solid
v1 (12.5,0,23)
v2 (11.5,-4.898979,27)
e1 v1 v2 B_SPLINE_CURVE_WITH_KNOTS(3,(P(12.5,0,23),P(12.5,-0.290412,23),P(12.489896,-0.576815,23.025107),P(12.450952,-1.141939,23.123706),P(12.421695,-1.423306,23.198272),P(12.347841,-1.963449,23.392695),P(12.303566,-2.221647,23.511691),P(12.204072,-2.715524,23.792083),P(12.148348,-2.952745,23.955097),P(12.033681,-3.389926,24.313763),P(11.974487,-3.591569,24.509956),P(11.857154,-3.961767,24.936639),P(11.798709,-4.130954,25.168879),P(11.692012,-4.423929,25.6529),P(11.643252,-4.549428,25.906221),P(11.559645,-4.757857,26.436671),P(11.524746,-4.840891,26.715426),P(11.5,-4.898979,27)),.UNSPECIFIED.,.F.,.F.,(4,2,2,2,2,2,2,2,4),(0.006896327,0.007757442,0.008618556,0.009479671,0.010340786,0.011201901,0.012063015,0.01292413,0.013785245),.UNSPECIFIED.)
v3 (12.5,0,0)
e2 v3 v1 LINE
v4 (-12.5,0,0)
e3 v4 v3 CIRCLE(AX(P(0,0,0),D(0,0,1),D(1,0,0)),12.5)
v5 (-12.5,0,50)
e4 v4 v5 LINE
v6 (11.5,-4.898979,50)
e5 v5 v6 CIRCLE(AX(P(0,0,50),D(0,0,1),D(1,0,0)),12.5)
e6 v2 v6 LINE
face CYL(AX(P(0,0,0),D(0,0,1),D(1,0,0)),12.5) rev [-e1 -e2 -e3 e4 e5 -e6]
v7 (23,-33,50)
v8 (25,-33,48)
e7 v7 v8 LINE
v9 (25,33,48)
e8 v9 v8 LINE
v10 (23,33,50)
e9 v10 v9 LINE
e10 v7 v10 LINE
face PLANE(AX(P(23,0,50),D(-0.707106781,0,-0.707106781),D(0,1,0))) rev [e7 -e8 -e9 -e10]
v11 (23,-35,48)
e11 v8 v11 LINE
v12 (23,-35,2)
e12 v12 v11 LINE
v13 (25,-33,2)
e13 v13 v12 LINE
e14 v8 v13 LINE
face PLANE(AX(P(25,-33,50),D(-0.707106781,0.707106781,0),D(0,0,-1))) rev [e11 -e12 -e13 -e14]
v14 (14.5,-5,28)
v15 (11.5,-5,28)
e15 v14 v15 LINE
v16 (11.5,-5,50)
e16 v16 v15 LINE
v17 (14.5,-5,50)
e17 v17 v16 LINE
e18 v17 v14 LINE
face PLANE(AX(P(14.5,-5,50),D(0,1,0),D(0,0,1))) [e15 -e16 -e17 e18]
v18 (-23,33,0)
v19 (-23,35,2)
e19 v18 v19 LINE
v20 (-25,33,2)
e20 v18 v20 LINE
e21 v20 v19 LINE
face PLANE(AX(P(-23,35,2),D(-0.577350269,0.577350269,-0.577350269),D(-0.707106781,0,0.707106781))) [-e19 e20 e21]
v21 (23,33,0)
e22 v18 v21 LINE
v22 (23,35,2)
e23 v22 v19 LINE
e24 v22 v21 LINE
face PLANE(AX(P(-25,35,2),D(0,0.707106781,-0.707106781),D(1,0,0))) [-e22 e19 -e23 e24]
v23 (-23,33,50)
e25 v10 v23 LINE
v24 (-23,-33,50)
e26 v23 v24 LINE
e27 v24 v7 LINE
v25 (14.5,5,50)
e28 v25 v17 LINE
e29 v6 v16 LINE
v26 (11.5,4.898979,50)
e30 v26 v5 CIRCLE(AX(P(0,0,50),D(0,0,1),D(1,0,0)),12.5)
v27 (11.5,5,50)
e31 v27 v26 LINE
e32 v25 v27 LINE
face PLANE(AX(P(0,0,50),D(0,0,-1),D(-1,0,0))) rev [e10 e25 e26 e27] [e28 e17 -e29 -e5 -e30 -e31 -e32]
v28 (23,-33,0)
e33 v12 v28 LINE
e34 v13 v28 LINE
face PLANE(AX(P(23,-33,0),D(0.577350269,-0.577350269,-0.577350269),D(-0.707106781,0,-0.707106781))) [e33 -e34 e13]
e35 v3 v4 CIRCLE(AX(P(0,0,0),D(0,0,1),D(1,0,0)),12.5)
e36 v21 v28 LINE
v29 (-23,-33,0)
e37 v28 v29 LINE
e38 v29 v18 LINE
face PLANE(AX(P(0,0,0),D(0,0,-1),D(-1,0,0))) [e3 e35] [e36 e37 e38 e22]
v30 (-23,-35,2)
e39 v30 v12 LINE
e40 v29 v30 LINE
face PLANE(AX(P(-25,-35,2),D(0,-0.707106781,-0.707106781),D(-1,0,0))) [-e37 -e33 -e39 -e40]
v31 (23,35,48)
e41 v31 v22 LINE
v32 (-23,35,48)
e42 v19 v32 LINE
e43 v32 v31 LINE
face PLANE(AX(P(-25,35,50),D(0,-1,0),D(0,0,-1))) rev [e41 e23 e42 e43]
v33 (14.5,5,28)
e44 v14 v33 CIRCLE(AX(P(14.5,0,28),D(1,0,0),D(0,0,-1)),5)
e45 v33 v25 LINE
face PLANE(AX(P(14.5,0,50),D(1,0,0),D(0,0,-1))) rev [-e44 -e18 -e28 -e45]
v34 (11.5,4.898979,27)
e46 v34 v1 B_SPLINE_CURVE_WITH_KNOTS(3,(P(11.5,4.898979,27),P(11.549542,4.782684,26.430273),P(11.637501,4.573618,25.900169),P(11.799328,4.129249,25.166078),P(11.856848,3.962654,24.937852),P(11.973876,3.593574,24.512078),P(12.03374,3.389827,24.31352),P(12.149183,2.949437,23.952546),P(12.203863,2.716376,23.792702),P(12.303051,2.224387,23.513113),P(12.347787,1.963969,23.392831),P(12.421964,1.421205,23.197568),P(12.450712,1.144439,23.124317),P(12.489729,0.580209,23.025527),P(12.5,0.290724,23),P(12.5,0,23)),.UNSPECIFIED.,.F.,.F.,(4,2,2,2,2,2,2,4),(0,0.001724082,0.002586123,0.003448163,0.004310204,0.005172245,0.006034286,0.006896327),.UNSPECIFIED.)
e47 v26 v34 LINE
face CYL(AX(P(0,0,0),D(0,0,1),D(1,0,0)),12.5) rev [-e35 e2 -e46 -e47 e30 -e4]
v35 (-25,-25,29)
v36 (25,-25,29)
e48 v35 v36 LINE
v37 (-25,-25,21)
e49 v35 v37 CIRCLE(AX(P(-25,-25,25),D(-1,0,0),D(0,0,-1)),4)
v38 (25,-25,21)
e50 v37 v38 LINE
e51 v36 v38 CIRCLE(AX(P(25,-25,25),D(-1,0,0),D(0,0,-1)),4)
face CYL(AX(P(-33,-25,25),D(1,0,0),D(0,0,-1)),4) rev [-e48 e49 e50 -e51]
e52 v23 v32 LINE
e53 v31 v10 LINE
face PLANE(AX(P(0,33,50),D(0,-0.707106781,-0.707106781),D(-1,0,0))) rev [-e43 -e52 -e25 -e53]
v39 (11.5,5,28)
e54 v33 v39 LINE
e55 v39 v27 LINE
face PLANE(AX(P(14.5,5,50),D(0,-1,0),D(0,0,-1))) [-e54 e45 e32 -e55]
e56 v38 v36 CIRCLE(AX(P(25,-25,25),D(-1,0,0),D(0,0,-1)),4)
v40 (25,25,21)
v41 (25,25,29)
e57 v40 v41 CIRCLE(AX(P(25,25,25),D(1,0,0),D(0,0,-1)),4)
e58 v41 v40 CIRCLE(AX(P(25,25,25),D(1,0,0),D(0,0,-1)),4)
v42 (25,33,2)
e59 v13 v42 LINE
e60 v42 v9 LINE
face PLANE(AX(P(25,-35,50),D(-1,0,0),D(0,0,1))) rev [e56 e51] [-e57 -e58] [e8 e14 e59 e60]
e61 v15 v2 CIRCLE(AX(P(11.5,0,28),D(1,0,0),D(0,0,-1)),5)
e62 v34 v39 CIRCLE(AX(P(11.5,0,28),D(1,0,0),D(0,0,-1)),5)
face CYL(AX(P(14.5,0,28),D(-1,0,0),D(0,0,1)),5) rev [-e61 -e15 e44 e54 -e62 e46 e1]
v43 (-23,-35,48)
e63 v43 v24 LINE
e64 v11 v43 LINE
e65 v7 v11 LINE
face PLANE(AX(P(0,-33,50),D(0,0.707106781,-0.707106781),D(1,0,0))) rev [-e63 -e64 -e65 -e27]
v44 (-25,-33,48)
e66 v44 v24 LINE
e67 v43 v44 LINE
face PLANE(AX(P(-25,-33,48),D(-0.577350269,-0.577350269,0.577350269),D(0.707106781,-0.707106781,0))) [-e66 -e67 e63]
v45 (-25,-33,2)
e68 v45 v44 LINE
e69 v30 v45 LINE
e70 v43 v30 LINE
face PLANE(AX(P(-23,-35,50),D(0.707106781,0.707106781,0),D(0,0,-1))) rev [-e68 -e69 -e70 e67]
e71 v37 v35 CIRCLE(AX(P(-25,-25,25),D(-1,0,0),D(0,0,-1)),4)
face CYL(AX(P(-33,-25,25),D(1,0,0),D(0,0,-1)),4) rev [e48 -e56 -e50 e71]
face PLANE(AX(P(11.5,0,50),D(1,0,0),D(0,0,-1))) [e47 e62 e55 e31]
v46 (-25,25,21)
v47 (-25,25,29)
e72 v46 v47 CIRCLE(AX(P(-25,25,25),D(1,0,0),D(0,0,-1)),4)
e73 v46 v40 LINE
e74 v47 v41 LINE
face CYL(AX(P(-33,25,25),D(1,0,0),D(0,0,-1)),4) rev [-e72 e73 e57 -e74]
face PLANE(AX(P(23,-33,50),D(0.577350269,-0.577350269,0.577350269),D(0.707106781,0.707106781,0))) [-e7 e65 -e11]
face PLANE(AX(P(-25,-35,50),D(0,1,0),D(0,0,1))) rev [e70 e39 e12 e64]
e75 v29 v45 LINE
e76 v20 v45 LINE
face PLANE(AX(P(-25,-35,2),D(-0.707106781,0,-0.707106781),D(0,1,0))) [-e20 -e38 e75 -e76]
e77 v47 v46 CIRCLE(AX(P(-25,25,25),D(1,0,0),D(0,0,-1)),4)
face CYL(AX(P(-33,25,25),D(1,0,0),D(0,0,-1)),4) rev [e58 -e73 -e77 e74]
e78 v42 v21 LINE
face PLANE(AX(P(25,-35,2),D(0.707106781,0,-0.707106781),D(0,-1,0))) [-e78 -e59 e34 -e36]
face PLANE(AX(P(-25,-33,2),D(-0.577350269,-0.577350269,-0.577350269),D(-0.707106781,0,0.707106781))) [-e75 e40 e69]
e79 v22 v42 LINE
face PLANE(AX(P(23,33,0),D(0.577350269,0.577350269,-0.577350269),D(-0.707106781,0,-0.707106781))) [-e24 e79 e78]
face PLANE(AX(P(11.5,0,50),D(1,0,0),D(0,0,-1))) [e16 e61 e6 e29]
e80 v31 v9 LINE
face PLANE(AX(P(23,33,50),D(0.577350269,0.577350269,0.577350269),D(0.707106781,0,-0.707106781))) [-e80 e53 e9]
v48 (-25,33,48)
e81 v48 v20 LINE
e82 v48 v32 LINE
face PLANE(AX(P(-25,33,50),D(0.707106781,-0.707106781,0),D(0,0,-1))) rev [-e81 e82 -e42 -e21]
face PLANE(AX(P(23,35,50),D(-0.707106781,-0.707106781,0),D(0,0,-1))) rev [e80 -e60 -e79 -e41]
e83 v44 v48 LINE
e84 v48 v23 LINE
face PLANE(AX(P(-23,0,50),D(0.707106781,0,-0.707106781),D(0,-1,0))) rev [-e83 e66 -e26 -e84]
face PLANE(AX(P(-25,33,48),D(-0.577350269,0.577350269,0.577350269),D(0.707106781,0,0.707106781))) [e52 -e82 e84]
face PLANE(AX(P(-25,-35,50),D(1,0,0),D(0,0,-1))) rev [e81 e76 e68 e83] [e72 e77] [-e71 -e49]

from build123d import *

# Parameters (mm, degrees)
SKETCH_1_W          = 50
SKETCH_1_H          = 70
EXTRUDE_1_DEPTH     = 50
SKETCH_2_R          = 12.5
CUT_EXTRUDE_1_DEPTH = 66.954529791
SKETCH_12_R         = 4
CUT_EXTRUDE_5_DEPTH = 58
CHAMFER_1_SIZE      = 2
CUT_EXTRUDE_START   = -13.5
CUT_EXTRUDE_6_DEPTH = 3


with BuildPart() as part:
    # 草图1 → 凸台-拉伸1 (new body)
    with BuildSketch(Plane.XY):
        Rectangle(SKETCH_1_W, SKETCH_1_H)
    extrude(amount=EXTRUDE_1_DEPTH)

    # 草图2 → 切除-拉伸1 (cut, through all)
    with BuildSketch(Plane.XY.offset(50)):
        Circle(SKETCH_2_R)
    extrude(amount=-CUT_EXTRUDE_1_DEPTH, mode=Mode.SUBTRACT)

    # 草图12 → 切除-拉伸5 (cut)
    with BuildSketch(Plane(origin=(25, 0, 0), x_dir=(0, 0, -1), z_dir=(1, 0, 0))):
        with Locations((-25, 25)):
            Circle(SKETCH_12_R)
    cut_extrude_5 = extrude(amount=-CUT_EXTRUDE_5_DEPTH, mode=Mode.SUBTRACT)

    # 镜向1: 切除-拉伸5 across plane
    add(cut_extrude_5.mirror(Plane.ZX), mode=Mode.SUBTRACT)

    # 倒角1
    chamfer_1_edges = [part.edges().sort_by_distance(p)[0] for p in [
        (-25, 0, 50),
        (0, -35, 50),
        (25, 0, 50),
        (0, -35, 0),
        (-25, 0, 0),
        (0, 35, 0),
        (25, 0, 0),
        (25, -35, 25),
        (-25, -35, 25),
        (-25, 35, 25),
        (25, 35, 25),
        (0, 35, 50),
    ]]
    chamfer(chamfer_1_edges, length=CHAMFER_1_SIZE)

    # 草图13 → 切除-拉伸6 (cut)
    with BuildSketch(Plane(origin=(25, 0, 0), x_dir=(0, 0, -1), z_dir=(1, 0, 0)).offset(CUT_EXTRUDE_START)):
        with BuildLine():
            Line((-50, 5), (-28, 5))
            ThreePointArc((-28, 5), (-23, 0), (-28, -5))
            Line((-28, -5), (-50, -5))
            ThreePointArc((-50, -5), (-55, 0), (-50, 5))
        make_face()
    extrude(amount=CUT_EXTRUDE_6_DEPTH, mode=Mode.SUBTRACT)


solid = part.part
